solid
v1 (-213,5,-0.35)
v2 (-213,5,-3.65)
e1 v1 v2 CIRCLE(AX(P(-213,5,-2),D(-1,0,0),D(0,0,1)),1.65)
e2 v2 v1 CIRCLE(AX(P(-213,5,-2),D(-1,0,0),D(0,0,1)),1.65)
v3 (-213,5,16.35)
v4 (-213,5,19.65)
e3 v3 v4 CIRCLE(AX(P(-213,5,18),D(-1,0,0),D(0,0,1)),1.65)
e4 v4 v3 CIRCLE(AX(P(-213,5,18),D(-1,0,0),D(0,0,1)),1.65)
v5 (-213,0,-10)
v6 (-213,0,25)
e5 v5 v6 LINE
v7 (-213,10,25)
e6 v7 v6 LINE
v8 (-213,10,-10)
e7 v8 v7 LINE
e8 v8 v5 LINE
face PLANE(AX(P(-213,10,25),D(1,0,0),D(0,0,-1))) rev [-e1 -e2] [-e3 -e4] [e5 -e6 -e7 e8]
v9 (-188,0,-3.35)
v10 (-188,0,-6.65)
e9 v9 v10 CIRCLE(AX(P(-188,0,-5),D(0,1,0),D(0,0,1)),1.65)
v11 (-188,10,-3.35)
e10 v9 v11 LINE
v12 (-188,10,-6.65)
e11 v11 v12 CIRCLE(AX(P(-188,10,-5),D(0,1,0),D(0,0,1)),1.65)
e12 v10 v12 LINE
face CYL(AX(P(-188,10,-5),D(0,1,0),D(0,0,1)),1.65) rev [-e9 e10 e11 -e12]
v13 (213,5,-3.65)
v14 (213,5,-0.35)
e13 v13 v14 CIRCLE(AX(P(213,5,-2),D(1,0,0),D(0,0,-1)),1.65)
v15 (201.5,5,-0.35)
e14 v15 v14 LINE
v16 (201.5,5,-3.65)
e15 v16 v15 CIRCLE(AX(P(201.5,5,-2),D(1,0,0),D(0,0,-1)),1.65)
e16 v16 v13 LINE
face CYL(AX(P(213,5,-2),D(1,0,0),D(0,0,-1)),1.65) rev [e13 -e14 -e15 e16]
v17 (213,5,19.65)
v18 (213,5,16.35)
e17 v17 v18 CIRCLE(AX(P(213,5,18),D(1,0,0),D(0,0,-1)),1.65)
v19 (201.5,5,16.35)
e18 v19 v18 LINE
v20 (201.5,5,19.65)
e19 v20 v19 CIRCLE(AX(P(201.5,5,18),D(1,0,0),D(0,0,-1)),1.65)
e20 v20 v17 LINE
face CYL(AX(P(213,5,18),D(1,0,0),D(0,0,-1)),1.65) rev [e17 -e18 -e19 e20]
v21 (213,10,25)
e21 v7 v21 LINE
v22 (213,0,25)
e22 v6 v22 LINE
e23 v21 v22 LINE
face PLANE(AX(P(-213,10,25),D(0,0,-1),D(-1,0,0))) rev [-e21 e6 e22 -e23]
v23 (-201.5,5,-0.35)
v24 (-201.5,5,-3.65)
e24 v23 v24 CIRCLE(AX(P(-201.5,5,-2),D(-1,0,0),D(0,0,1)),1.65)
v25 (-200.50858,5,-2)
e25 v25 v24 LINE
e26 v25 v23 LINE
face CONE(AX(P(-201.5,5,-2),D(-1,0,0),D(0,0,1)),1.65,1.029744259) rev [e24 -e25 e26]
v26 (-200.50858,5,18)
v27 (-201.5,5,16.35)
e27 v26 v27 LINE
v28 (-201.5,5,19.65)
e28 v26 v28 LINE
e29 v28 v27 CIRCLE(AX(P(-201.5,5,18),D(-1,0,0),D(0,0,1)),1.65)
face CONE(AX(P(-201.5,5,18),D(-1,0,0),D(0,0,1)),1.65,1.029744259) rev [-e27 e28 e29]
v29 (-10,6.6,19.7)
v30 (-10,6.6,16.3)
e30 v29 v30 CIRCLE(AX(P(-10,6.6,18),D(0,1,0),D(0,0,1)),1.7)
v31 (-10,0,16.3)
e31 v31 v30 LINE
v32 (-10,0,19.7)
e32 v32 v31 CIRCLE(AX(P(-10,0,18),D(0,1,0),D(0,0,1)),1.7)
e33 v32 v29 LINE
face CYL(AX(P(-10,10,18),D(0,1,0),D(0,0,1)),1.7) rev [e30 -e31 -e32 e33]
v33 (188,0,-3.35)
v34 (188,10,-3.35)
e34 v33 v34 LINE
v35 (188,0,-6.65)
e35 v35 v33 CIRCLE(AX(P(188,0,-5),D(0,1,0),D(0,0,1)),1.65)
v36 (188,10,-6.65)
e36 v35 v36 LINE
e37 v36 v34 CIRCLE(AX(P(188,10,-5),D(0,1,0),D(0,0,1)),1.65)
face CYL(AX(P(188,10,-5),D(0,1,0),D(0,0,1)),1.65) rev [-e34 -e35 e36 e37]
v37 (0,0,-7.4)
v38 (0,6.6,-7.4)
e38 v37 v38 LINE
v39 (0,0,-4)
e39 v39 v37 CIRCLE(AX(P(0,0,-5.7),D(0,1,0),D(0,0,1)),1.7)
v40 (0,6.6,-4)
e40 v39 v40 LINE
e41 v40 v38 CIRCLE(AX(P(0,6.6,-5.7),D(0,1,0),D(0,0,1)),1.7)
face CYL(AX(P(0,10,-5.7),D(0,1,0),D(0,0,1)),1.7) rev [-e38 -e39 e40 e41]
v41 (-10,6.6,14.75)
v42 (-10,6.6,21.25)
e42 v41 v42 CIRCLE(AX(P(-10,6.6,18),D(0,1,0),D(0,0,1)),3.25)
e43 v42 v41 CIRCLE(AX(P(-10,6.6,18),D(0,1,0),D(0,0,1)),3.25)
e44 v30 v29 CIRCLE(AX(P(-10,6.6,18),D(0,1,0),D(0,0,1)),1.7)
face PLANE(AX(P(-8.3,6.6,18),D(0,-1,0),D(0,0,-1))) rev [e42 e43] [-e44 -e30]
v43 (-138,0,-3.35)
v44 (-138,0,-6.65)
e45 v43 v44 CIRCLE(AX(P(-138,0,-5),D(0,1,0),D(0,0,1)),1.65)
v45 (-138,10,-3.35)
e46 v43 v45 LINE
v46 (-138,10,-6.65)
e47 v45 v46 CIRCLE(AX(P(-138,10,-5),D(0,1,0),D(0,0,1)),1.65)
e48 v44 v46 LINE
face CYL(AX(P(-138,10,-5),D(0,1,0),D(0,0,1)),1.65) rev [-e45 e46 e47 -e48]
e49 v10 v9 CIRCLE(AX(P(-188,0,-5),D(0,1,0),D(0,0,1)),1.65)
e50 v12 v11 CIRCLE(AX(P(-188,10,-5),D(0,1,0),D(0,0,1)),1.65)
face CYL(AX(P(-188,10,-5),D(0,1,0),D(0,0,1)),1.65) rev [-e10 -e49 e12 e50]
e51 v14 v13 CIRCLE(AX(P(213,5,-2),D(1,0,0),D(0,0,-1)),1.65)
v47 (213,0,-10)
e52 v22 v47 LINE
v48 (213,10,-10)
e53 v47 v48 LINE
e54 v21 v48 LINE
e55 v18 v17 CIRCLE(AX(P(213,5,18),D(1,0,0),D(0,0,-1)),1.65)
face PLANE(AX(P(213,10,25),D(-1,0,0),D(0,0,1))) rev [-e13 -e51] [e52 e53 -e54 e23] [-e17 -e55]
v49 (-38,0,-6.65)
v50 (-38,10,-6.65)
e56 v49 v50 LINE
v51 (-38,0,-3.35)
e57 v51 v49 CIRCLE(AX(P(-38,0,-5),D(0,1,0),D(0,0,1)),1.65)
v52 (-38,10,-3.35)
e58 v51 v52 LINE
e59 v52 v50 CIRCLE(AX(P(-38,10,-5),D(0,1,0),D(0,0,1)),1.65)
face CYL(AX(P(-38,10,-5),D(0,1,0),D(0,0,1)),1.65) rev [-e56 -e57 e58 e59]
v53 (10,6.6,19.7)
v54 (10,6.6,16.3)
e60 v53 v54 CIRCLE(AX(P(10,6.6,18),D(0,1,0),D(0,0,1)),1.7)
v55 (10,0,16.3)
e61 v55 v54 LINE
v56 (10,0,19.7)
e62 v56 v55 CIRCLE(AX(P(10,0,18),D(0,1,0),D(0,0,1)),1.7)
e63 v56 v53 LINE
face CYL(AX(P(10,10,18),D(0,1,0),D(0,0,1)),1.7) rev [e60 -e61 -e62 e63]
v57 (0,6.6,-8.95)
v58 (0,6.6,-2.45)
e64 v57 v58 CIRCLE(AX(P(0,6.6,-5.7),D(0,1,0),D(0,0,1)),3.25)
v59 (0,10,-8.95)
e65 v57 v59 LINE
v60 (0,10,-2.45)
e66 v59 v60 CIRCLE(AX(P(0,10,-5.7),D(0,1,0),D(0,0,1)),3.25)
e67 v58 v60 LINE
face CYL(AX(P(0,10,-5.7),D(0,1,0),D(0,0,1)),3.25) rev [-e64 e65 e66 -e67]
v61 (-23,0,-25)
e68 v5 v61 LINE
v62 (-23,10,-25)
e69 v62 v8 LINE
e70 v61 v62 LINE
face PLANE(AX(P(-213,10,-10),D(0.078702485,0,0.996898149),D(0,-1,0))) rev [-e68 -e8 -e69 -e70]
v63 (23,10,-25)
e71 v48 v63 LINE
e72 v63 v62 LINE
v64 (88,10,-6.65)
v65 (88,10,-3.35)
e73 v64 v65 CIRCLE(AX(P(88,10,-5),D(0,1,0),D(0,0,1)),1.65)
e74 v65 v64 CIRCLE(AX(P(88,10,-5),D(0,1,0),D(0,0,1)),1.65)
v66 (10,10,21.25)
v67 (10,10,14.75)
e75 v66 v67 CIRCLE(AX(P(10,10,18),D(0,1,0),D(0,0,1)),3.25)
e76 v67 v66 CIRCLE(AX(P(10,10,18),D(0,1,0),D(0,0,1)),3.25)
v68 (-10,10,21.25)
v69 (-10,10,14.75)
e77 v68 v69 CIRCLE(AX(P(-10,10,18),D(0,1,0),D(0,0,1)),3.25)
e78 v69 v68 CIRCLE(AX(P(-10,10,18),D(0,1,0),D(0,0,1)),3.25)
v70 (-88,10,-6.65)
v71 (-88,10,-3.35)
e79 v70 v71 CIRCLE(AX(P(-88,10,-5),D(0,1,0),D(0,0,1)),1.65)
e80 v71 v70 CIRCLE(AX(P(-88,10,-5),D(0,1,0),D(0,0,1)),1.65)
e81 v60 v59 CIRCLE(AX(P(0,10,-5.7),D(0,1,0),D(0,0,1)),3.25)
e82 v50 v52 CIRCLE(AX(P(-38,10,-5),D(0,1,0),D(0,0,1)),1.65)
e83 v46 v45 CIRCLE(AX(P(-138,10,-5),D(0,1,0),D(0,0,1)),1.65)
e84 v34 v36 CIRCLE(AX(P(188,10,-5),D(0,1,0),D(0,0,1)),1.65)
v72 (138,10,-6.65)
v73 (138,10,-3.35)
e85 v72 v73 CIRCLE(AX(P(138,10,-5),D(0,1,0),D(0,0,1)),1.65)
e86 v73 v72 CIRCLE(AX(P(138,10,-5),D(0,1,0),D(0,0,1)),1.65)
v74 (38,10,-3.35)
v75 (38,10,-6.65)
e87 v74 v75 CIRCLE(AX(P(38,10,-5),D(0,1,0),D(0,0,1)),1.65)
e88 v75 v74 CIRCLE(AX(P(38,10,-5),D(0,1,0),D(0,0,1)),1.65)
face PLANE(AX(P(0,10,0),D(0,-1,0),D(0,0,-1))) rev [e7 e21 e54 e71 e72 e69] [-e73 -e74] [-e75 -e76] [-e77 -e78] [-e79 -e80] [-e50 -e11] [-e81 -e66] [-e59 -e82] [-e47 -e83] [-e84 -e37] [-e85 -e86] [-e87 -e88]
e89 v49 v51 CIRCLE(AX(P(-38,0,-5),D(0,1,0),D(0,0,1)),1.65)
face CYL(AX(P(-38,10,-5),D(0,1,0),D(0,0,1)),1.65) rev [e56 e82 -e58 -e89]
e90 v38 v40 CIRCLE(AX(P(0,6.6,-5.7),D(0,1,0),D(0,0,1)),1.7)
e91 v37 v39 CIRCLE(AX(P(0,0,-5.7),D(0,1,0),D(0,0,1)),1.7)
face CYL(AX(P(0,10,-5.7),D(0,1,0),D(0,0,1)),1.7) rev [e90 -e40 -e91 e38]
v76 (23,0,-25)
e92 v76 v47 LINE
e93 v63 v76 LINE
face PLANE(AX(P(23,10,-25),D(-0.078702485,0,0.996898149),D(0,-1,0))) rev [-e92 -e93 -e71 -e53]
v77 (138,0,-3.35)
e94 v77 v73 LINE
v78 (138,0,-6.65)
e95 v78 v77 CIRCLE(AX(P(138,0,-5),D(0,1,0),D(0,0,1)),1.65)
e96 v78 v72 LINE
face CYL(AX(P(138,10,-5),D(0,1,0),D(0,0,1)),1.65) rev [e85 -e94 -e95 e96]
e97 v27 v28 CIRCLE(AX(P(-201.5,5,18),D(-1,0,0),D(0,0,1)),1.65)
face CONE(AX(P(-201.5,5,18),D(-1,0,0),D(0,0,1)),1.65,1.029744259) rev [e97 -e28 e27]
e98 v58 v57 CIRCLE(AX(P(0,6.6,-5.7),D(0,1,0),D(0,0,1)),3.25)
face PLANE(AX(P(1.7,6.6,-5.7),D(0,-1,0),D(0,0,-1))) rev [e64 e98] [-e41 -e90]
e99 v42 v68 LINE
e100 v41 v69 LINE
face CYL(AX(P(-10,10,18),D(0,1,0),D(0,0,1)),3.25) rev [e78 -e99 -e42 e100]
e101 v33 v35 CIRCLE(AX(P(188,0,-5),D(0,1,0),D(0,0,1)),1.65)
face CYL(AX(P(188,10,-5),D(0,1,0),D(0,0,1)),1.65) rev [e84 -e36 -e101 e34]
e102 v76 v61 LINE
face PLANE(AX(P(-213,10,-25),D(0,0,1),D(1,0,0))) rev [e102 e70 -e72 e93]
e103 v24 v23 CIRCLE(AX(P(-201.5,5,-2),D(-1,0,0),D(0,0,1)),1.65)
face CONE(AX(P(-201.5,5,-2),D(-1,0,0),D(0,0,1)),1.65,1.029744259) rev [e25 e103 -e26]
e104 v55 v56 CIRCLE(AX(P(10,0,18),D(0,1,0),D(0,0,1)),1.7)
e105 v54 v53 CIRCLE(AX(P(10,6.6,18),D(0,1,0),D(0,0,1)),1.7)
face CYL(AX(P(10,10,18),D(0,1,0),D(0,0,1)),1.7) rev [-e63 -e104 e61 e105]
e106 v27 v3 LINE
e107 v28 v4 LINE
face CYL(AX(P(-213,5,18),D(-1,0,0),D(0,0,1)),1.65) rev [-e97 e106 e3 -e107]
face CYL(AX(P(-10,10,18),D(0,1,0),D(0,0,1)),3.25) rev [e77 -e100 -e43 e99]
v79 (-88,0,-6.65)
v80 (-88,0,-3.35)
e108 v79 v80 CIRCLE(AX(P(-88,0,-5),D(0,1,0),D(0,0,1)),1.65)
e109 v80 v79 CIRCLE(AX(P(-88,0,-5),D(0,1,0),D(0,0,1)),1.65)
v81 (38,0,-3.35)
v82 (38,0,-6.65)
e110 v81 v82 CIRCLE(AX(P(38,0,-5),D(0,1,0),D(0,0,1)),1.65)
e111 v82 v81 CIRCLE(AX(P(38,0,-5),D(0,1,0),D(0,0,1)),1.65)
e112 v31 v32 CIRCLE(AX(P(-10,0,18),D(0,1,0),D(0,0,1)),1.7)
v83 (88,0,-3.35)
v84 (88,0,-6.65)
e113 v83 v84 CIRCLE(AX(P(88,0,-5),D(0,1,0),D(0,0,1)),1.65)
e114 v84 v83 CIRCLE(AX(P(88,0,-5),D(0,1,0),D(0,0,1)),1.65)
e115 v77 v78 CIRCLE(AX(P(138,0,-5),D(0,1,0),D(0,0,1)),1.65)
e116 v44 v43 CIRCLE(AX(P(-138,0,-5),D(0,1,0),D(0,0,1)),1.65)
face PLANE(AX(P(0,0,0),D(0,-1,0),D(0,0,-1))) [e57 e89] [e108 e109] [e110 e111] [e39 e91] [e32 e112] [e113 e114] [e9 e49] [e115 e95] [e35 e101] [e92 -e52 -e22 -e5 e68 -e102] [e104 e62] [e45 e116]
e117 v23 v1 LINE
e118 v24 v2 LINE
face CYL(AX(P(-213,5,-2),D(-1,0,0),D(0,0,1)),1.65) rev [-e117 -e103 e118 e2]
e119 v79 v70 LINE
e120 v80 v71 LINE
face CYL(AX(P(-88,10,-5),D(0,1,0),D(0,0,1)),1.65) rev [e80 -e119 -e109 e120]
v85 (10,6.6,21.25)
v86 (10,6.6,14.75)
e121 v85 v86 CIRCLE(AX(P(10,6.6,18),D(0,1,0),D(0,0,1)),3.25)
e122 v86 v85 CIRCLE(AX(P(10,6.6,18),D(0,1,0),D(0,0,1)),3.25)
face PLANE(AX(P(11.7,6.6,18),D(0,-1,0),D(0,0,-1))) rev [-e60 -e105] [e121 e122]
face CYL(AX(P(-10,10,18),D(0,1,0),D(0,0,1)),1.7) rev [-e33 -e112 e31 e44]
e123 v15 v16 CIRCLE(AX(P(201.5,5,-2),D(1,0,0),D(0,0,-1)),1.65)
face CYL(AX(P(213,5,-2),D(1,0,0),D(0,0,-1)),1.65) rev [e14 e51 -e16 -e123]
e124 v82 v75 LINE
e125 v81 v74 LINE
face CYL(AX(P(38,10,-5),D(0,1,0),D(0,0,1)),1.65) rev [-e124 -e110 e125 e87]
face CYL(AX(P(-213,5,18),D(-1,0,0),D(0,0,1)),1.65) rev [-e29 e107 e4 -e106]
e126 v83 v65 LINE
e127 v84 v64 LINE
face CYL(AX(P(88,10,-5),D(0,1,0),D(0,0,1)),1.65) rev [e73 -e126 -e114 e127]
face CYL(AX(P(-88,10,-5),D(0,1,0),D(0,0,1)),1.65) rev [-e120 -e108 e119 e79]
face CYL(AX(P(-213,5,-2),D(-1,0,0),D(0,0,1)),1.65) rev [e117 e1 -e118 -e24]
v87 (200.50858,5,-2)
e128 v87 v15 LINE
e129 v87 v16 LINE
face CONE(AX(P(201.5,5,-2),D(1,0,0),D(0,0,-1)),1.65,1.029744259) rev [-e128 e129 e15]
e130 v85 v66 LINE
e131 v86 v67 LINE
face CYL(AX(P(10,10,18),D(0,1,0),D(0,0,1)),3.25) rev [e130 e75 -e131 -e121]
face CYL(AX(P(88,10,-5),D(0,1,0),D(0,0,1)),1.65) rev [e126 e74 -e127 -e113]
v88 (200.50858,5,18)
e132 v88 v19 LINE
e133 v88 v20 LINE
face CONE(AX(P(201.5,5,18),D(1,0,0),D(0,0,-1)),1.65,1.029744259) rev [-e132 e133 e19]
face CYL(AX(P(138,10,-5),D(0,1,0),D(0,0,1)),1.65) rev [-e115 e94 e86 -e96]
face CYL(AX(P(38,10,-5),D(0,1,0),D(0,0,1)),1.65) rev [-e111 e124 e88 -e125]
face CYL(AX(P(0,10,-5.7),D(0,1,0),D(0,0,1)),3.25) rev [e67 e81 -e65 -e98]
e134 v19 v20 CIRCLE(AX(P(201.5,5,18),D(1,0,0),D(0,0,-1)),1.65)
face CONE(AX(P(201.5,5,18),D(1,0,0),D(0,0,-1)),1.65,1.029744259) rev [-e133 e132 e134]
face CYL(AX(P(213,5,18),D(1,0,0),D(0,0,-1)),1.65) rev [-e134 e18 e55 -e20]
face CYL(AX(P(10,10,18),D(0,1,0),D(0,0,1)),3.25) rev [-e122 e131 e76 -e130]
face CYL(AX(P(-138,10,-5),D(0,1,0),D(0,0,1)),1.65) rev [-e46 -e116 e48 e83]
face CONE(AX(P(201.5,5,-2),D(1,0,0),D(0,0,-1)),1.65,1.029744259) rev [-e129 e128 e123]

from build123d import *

# Parameters (mm, degrees)
SKETCH_1_W                   = 426
SKETCH_1_H                   = 50
EXTRUDE_1_DEPTH              = 10
HOLE_WIZARD_M4_1_AT_2_COUNT  = 2
HOLE_WIZARD_M4_1_AT_2_PITCH  = 20
HOLE_WIZARD_M3_1_D           = 3.4
HOLE_WIZARD_M3_1_CBORE_D     = 6.5
HOLE_WIZARD_M3_1_CBORE_DEPTH = 3.4
HOLE_WIZARD_M4_2_D           = 3.3
CHAMFER_1_SIZE               = 15
CHAMFER_1_SIZE2              = 190
CHAMFER_2_SIZE               = 190
CHAMFER_2_SIZE2              = 15


with BuildPart() as part:
    # 草图1 → 凸台-拉伸1 (new body)
    with BuildSketch(Plane(origin=(0, 0, 0), x_dir=(1, 0, 0), z_dir=(0, 1, 0))):
        Rectangle(SKETCH_1_W, SKETCH_1_H)
    extrude(amount=EXTRUDE_1_DEPTH)

    # 草图3 → M4 螺纹孔1 (revolve, cut)
    with BuildSketch(Plane(origin=(-213, 5, -2), x_dir=(0, 0, 1), z_dir=(0, 1, 0))):
        Polygon((0, 0), (0, 12.491420021), (1.65, 11.5), (1.65, 0), align=None)
    hole_wizard_m4_1 = revolve(axis=Axis((-219.35, 5, -2), (1, 0, 0)), mode=Mode.SUBTRACT)

    # M4 螺纹孔1 at 2: M4 螺纹孔1 ×2
    with Locations(*[(0, 0, i * HOLE_WIZARD_M4_1_AT_2_PITCH) for i in range(1, HOLE_WIZARD_M4_1_AT_2_COUNT)]):
        add(hole_wizard_m4_1, mode=Mode.SUBTRACT)

    # 镜向1: M4 螺纹孔1 across plane
    add(hole_wizard_m4_1.mirror(Plane(origin=(0, 0, 0), x_dir=(0, 0, 1), z_dir=(1, 0, 0))), mode=Mode.SUBTRACT)

    # 镜向1 copy 1 sketch → 镜向1 copy 1 (revolve, cut)
    with BuildSketch(Plane(origin=(213, 5, 18), x_dir=(0, 0, 1), z_dir=(0, 1, 0))):
        Polygon((0, 0), (0, -12.491420021), (1.65, -11.5), (1.65, 0), align=None)
    revolve(axis=Axis((219.35, 5, 18), (1, 0, 0)), mode=Mode.SUBTRACT)

    # M3 六角凹头螺钉的柱形沉头孔1 (through all)
    with Locations(Plane(origin=(0, 10, 0), x_dir=(1, 0, 0), z_dir=(0, 1, 0))):
        with Locations((10, -18), (-10, -18), (0, 5.7)):
            CounterBoreHole(HOLE_WIZARD_M3_1_D / 2, HOLE_WIZARD_M3_1_CBORE_D / 2, HOLE_WIZARD_M3_1_CBORE_DEPTH)

    # M4 螺纹孔2 (through all)
    with Locations(Plane(origin=(0, 10, 0), x_dir=(1, 0, 0), z_dir=(0, 1, 0))):
        with Locations((-38, 5), (-88, 5), (-138, 5), (-188, 5)):
            hole_wizard_m4_2 = Hole(HOLE_WIZARD_M4_2_D / 2)

    # 镜向2: M4 螺纹孔2 across plane
    add(hole_wizard_m4_2.mirror(Plane(origin=(0, 0, 0), x_dir=(0, 0, 1), z_dir=(1, 0, 0))), mode=Mode.SUBTRACT)

    # 倒角1
    chamfer_1_edges = [part.edges().sort_by_distance(p)[0] for p in [
        (213, 5, -25),
    ]]
    chamfer_1_side = [part.faces().sort_by_distance(p)[0] for p in [
        (213, 5, -0.283390906),
    ]]
    chamfer(chamfer_1_edges, length=CHAMFER_1_SIZE, length2=CHAMFER_1_SIZE2, reference=chamfer_1_side[0])

    # 倒角2
    chamfer_2_edges = [part.edges().sort_by_distance(p)[0] for p in [
        (-213, 5, -25),
    ]]
    chamfer_2_side = [part.faces().sort_by_distance(p)[0] for p in [
        (-95, 5, -25),
    ]]
    chamfer(chamfer_2_edges, length=CHAMFER_2_SIZE, length2=CHAMFER_2_SIZE2, reference=chamfer_2_side[0])


solid = part.part
